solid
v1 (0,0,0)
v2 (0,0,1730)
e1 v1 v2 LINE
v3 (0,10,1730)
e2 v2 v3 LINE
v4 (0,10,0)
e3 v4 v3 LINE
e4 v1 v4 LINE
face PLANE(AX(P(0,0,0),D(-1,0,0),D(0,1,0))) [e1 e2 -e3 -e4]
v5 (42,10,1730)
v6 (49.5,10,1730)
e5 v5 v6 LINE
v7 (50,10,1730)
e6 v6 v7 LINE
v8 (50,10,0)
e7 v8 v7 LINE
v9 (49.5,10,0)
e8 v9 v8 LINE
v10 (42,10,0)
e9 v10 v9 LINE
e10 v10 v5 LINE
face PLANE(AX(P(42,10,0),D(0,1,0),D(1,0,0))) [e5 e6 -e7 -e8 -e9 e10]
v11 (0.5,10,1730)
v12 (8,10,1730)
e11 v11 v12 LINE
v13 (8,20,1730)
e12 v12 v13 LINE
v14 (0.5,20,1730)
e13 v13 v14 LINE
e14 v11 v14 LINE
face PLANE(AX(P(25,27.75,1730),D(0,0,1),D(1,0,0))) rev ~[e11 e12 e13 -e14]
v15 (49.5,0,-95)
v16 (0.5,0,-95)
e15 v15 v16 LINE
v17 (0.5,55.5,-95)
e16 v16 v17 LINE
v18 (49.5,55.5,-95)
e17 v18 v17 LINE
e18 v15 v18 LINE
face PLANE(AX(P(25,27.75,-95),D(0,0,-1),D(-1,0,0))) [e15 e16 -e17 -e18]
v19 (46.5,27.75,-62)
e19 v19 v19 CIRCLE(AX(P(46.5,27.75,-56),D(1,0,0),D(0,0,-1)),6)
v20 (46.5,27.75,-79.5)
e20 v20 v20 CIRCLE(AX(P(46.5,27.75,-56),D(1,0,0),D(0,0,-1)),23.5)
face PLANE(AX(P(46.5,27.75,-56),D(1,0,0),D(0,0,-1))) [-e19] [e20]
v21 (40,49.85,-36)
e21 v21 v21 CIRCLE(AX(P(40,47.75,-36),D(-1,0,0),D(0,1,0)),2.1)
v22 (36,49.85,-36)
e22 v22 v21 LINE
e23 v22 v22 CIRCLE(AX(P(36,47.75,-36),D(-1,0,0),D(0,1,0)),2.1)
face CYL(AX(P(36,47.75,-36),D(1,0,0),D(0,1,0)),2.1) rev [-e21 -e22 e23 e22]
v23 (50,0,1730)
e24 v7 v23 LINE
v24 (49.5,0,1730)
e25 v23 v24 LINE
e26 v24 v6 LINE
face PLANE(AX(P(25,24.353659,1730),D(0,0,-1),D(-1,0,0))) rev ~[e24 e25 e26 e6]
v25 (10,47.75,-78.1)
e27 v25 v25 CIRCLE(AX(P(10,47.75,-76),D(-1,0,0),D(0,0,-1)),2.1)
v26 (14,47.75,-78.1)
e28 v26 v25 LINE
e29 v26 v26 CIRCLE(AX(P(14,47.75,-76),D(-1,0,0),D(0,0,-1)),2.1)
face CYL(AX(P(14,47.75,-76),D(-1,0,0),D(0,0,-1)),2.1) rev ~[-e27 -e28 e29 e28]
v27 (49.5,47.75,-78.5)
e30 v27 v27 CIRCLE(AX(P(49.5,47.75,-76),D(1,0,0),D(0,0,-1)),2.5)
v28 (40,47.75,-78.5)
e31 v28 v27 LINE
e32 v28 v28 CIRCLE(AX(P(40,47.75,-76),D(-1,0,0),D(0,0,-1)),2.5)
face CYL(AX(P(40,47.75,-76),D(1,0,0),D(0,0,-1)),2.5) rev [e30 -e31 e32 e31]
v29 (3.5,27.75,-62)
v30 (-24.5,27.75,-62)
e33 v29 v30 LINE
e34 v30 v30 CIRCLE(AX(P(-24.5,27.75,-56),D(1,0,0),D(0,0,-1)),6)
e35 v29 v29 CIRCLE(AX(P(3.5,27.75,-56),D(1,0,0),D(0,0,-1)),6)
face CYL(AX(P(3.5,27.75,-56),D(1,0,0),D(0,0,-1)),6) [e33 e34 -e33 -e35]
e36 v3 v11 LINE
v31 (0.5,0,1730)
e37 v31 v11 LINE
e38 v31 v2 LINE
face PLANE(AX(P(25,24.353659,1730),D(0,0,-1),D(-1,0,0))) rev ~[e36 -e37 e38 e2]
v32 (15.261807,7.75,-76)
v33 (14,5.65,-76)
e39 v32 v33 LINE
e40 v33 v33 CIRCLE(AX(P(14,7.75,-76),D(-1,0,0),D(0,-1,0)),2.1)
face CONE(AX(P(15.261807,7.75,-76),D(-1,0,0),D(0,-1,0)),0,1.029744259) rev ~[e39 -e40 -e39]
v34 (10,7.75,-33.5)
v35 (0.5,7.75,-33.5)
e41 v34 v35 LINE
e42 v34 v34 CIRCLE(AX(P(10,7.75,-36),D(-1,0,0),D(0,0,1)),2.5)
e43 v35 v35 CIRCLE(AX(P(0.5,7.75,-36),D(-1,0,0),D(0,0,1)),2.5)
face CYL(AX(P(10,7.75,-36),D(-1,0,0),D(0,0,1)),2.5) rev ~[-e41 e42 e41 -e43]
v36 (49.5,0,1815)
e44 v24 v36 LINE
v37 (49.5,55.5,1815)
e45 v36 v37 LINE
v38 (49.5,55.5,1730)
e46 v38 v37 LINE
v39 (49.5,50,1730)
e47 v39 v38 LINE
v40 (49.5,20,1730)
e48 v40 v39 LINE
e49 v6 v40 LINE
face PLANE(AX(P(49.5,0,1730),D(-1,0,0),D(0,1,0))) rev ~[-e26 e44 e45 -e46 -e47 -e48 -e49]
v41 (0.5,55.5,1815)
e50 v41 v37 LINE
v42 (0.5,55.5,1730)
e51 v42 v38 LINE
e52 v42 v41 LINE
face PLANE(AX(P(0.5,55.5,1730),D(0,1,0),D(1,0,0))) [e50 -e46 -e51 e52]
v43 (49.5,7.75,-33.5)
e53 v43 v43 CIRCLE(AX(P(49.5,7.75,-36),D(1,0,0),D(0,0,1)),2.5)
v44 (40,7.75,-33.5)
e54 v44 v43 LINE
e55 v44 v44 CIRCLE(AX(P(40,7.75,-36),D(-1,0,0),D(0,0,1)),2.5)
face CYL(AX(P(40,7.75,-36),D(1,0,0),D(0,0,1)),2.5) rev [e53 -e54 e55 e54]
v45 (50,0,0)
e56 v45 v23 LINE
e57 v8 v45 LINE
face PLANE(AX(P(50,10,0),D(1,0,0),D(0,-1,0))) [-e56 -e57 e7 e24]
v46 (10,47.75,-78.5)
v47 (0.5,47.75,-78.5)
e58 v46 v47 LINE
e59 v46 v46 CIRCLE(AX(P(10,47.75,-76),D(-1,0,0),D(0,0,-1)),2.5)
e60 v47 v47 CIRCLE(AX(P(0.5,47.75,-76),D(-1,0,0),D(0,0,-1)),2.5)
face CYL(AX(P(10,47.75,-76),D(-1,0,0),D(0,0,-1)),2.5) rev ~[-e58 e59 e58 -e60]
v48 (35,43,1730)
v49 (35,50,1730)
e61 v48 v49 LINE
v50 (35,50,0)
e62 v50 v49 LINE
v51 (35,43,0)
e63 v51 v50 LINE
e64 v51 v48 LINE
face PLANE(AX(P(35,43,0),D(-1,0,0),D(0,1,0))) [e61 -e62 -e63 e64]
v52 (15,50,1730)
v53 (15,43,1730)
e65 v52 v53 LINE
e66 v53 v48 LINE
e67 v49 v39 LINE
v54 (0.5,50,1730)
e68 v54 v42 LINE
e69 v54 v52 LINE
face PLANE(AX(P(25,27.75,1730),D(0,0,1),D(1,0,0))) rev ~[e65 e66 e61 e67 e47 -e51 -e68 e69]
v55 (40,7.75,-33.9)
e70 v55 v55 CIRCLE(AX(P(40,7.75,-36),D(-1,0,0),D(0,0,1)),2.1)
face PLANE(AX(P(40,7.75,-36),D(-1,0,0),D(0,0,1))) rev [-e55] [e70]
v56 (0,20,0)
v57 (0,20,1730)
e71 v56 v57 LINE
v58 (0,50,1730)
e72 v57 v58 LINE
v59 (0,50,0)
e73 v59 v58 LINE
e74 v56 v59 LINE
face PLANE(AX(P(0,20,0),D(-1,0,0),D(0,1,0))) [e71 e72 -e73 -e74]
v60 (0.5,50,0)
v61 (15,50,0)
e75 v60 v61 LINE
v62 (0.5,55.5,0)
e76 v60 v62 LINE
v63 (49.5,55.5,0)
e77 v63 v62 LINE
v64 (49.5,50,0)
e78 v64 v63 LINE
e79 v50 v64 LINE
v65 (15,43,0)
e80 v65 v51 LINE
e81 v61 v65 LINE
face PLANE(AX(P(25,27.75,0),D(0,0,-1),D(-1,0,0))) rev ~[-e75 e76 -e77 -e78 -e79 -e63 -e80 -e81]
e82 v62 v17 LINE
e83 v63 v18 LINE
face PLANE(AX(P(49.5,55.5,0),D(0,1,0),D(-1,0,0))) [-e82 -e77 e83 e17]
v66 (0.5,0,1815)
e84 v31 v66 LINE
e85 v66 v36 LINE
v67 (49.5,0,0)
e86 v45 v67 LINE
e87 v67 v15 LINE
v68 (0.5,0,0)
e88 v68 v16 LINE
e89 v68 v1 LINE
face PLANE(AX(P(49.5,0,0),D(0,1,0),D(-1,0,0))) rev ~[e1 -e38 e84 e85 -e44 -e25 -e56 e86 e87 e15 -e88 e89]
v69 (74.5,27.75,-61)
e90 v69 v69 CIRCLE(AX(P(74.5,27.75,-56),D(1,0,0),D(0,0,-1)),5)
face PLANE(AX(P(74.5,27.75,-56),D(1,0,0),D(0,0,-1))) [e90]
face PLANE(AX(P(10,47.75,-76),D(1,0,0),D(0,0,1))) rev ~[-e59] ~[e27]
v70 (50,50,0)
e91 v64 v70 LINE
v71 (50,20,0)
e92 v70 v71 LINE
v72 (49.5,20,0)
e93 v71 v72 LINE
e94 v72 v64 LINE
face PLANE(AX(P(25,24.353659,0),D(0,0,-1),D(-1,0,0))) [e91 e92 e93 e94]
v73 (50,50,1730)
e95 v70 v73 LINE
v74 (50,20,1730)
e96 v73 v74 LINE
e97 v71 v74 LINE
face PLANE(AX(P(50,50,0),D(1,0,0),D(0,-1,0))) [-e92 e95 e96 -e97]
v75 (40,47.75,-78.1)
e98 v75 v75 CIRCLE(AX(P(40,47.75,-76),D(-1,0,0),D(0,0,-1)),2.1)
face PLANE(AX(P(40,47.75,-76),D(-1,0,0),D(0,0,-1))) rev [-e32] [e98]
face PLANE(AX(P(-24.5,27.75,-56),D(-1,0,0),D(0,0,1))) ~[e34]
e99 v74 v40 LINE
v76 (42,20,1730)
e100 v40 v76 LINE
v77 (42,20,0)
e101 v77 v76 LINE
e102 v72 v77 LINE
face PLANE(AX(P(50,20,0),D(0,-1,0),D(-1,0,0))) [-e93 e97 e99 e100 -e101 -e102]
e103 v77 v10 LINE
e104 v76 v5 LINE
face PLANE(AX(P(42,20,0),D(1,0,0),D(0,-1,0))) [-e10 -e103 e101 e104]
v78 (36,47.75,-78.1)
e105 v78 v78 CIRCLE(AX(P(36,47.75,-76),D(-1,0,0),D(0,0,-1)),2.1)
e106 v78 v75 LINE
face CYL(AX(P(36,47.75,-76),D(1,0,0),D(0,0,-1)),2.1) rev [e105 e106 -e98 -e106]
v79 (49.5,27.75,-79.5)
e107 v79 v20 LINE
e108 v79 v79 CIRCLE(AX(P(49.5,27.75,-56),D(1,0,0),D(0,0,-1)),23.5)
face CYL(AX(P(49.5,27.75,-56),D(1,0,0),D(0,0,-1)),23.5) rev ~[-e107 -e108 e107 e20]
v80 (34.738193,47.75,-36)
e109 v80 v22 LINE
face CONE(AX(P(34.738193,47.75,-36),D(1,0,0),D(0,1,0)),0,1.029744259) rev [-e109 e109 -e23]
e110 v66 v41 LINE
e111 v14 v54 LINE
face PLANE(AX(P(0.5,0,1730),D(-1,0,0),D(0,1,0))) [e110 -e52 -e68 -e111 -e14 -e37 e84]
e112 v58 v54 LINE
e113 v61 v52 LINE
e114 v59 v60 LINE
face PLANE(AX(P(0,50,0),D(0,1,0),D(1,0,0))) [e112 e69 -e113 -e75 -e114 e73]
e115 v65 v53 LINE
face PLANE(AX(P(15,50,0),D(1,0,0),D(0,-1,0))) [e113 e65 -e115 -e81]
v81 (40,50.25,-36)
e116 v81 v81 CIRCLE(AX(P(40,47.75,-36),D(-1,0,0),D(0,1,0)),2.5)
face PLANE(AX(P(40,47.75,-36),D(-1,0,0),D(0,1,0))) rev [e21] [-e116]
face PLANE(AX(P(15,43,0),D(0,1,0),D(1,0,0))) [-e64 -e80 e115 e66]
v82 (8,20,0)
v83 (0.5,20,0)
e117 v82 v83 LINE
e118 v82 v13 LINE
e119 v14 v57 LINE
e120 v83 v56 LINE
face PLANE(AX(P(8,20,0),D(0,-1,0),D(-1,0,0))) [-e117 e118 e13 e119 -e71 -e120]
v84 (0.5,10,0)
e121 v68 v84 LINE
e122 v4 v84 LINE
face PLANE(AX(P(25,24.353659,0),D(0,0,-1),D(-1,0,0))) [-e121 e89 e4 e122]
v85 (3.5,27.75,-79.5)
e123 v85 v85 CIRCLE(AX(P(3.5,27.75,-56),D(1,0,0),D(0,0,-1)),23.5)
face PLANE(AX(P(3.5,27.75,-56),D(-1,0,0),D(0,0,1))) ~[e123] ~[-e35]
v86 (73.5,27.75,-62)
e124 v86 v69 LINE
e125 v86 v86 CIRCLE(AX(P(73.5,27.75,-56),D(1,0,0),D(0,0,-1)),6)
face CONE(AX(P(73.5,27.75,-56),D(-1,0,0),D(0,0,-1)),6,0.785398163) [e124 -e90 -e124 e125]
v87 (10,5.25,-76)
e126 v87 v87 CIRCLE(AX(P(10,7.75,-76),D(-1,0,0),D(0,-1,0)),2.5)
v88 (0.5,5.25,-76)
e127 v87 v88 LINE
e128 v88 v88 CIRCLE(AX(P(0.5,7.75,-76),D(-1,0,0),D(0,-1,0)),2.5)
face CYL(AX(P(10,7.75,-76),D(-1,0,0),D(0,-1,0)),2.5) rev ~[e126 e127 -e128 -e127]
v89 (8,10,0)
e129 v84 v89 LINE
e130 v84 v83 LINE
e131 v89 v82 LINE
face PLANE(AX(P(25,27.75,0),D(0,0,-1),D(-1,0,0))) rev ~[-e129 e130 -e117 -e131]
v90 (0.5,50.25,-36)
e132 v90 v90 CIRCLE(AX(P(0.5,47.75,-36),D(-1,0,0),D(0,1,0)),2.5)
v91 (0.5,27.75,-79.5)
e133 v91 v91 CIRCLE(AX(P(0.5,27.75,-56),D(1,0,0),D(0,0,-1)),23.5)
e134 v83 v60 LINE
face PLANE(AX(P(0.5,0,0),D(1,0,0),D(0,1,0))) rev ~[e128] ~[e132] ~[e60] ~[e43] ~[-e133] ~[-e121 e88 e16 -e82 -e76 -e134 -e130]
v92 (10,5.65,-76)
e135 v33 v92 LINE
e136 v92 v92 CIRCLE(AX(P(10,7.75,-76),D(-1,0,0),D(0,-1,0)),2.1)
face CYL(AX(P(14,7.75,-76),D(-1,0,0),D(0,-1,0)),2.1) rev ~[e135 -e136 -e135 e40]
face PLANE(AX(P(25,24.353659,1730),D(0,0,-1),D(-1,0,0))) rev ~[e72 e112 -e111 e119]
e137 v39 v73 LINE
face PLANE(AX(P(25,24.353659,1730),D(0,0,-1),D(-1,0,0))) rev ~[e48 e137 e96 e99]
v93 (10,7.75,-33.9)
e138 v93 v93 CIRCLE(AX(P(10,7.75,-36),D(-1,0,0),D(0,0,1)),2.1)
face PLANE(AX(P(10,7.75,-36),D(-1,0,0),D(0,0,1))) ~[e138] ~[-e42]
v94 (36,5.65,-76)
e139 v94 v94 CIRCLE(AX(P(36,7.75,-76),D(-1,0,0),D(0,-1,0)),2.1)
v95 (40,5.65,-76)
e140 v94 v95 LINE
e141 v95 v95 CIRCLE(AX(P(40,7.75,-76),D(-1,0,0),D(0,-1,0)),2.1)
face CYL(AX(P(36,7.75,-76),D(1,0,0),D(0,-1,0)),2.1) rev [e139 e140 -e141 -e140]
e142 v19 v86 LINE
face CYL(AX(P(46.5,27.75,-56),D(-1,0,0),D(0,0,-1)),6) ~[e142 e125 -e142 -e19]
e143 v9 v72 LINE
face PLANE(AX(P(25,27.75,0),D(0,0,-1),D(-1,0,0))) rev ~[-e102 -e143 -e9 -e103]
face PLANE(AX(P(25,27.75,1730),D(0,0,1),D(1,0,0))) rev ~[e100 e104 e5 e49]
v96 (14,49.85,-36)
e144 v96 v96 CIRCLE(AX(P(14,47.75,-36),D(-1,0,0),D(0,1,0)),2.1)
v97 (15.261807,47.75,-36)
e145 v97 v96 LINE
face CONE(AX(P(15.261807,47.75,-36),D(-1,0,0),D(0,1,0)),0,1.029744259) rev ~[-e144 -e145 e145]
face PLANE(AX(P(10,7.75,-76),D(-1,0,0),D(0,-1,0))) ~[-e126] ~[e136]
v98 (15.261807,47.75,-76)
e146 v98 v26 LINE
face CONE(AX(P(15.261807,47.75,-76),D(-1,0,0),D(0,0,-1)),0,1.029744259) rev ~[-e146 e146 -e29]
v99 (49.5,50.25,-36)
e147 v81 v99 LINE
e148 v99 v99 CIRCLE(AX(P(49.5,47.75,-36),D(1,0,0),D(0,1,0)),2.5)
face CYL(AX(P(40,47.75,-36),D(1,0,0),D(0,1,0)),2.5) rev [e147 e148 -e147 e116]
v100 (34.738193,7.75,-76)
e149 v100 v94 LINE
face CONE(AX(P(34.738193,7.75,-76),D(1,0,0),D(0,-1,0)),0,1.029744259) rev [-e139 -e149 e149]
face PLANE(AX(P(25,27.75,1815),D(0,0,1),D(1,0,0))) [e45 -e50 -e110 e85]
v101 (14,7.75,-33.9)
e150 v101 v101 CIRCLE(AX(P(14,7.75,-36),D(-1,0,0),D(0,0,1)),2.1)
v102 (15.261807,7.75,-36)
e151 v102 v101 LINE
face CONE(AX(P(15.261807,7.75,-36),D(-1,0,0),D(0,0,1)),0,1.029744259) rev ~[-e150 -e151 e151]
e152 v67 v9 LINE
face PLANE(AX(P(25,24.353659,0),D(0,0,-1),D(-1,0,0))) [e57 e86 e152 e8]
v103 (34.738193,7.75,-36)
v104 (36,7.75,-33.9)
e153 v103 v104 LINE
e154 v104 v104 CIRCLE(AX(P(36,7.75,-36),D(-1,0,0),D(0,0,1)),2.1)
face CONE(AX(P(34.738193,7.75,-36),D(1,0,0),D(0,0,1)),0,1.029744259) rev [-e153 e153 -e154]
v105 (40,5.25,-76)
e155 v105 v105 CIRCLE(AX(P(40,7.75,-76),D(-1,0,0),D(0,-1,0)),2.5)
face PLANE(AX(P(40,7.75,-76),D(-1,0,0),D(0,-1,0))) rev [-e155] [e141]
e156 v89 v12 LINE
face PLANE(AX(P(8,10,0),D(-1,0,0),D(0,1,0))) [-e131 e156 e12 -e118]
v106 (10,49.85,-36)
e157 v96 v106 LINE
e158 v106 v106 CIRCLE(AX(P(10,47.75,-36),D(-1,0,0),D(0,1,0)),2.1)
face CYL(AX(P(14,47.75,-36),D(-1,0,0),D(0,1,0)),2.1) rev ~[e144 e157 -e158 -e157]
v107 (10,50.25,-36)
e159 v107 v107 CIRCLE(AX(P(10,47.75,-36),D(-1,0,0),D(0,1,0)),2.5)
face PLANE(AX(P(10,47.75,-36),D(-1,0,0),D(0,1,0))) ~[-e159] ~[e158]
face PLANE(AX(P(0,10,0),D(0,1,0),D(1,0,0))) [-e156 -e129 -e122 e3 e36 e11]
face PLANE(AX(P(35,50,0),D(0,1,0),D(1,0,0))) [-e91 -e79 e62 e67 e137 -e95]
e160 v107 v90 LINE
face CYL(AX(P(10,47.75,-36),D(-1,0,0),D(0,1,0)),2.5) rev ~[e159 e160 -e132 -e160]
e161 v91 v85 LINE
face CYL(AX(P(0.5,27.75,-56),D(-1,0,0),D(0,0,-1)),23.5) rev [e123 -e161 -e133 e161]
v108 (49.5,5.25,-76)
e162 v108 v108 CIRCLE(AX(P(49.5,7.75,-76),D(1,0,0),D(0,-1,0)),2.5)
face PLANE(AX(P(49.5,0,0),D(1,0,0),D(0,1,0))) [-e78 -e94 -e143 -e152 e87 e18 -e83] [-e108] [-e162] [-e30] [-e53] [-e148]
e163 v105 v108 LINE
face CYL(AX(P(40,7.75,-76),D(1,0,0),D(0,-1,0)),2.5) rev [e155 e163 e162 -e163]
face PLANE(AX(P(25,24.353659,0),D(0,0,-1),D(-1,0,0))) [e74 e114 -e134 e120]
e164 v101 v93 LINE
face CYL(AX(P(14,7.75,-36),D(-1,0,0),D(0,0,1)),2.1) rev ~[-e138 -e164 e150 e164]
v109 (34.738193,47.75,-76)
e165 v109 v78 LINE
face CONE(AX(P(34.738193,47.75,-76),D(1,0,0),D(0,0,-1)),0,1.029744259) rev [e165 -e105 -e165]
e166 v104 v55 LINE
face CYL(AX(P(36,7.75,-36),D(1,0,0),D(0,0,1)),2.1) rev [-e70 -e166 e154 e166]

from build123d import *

# Parameters (mm, degrees)
EXTRUDE_671_DEPTH        = 1730
SKETCH_2_W               = 49
SKETCH_2_H               = 55.5
EXTRUDE_1_DEPTH          = 85
SKETCH_4_W               = 49
SKETCH_4_H               = 55.5
EXTRUDE_3_DEPTH          = 95
SKETCH_9_R               = 23.5
CUT_EXTRUDE_5_DEPTH      = 3
SKETCH_10_R              = 6
EXTRUDE_4_DEPTH          = 28
CHAMFER_1_SIZE           = 1
PATTERN_CIRCULAR_1_COUNT = 4


with BuildPart() as part:
    # 草图1 → Extrude 671 (new body)
    with BuildSketch(Plane.XY):
        Polygon((15, 50), (15, 43), (35, 43), (35, 50), (50, 50), (50, 20), (42, 20), (42, 10), (50, 10), (50, 0), (0, 0), (0, 10), (8, 10), (8, 20), (0, 20), (0, 50), align=None)
    extrude(amount=EXTRUDE_671_DEPTH)

    # 草图2 → 凸台-拉伸1 (add)
    with BuildSketch(Plane.XY.offset(1730)):
        with Locations((25, 27.75)):
            Rectangle(SKETCH_2_W, SKETCH_2_H)
    extrude(amount=EXTRUDE_1_DEPTH)

    # 草图4 → 凸台-拉伸3 (add)
    with BuildSketch(Plane(origin=(0, 0, 0), x_dir=(-1, 0, 0), z_dir=(0, 0, -1))):
        with Locations((-25, 27.75)):
            Rectangle(SKETCH_4_W, SKETCH_4_H)
    extrude(amount=EXTRUDE_3_DEPTH)

    # 草图9 → 切除-拉伸5 (cut)
    with BuildSketch(Plane(origin=(49.5, 0, 0), x_dir=(0, 0, -1), z_dir=(1, 0, 0))):
        with Locations((56, 27.75)):
            Circle(SKETCH_9_R)
    cut_extrude_5 = extrude(amount=-CUT_EXTRUDE_5_DEPTH, mode=Mode.SUBTRACT)

    # 草图10 → 凸台-拉伸4 (add)
    with BuildSketch(Plane(origin=(46.5, 0, 0), x_dir=(0, 0, -1), z_dir=(1, 0, 0))):
        with Locations((56, 27.75)):
            Circle(SKETCH_10_R)
    extrude_4 = extrude(amount=EXTRUDE_4_DEPTH)

    # 倒角1
    chamfer_1_edges = [part.edges().sort_by_distance(p)[0] for p in [
        (74.5, 27.75, -50),
    ]]
    chamfer(chamfer_1_edges, length=CHAMFER_1_SIZE)

    # 草图12 → M5 螺纹孔1 (revolve, cut)
    with BuildSketch(Plane(origin=(50, 47.75, -76), x_dir=(0, 0, -1), z_dir=(0, 1, 0))):
        Polygon((0, 0), (0, 15.2618073), (2.1, 14), (2.1, 10), (2.5, 10), (2.5, 0), align=None)
    hole_wizard_m5_1 = revolve(axis=Axis((56.35, 47.75, -76), (-1, 0, 0)), mode=Mode.SUBTRACT)

    # 阵列(圆周)1: M5 螺纹孔1 ×4 about axis
    pattern_circular_1_axis = Axis((0, 27.75, -56), (1, 0, 0))
    for i in range(1, PATTERN_CIRCULAR_1_COUNT):
        add(hole_wizard_m5_1.rotate(pattern_circular_1_axis, i * 360 / PATTERN_CIRCULAR_1_COUNT), mode=Mode.SUBTRACT)

    # 镜向1: 切除-拉伸5, 凸台-拉伸4, M5 螺纹孔1 across plane
    add(cut_extrude_5.mirror(Plane(origin=(25, 0, 0), x_dir=(0, 0, 1), z_dir=(1, 0, 0))), mode=Mode.SUBTRACT)
    add(extrude_4.mirror(Plane(origin=(25, 0, 0), x_dir=(0, 0, 1), z_dir=(1, 0, 0))))
    add(hole_wizard_m5_1.mirror(Plane(origin=(25, 0, 0), x_dir=(0, 0, 1), z_dir=(1, 0, 0))), mode=Mode.SUBTRACT)

    # 镜向1 copy 1 sketch → 镜向1 copy 1 (revolve, cut)
    with BuildSketch(Plane(origin=(0, 47.75, -36), x_dir=(0, 1, 0), z_dir=(0, 0, 1))):
        Polygon((0, 0), (0, -15.2618073), (2.1, -14), (2.1, -10), (2.5, -10), (2.5, 0), align=None)
    revolve(axis=Axis((-6.35, 47.75, -36), (-1, 0, 0)), mode=Mode.SUBTRACT)

    # 镜向1 copy 2 sketch → 镜向1 copy 2 (revolve, cut)
    with BuildSketch(Plane(origin=(0, 7.75, -36), x_dir=(0, 0, 1), z_dir=(0, -1, 0))):
        Polygon((0, 0), (0, -15.2618073), (2.1, -14), (2.1, -10), (2.5, -10), (2.5, 0), align=None)
    revolve(axis=Axis((-6.35, 7.75, -36), (-1, 0, 0)), mode=Mode.SUBTRACT)

    # 镜向1 copy 3 sketch → 镜向1 copy 3 (revolve, cut)
    with BuildSketch(Plane(origin=(0, 7.75, -76), x_dir=(0, -1, 0), z_dir=(0, 0, -1))):
        Polygon((0, 0), (0, -15.2618073), (2.1, -14), (2.1, -10), (2.5, -10), (2.5, 0), align=None)
    revolve(axis=Axis((-6.35, 7.75, -76), (-1, 0, 0)), mode=Mode.SUBTRACT)


solid = part.part
